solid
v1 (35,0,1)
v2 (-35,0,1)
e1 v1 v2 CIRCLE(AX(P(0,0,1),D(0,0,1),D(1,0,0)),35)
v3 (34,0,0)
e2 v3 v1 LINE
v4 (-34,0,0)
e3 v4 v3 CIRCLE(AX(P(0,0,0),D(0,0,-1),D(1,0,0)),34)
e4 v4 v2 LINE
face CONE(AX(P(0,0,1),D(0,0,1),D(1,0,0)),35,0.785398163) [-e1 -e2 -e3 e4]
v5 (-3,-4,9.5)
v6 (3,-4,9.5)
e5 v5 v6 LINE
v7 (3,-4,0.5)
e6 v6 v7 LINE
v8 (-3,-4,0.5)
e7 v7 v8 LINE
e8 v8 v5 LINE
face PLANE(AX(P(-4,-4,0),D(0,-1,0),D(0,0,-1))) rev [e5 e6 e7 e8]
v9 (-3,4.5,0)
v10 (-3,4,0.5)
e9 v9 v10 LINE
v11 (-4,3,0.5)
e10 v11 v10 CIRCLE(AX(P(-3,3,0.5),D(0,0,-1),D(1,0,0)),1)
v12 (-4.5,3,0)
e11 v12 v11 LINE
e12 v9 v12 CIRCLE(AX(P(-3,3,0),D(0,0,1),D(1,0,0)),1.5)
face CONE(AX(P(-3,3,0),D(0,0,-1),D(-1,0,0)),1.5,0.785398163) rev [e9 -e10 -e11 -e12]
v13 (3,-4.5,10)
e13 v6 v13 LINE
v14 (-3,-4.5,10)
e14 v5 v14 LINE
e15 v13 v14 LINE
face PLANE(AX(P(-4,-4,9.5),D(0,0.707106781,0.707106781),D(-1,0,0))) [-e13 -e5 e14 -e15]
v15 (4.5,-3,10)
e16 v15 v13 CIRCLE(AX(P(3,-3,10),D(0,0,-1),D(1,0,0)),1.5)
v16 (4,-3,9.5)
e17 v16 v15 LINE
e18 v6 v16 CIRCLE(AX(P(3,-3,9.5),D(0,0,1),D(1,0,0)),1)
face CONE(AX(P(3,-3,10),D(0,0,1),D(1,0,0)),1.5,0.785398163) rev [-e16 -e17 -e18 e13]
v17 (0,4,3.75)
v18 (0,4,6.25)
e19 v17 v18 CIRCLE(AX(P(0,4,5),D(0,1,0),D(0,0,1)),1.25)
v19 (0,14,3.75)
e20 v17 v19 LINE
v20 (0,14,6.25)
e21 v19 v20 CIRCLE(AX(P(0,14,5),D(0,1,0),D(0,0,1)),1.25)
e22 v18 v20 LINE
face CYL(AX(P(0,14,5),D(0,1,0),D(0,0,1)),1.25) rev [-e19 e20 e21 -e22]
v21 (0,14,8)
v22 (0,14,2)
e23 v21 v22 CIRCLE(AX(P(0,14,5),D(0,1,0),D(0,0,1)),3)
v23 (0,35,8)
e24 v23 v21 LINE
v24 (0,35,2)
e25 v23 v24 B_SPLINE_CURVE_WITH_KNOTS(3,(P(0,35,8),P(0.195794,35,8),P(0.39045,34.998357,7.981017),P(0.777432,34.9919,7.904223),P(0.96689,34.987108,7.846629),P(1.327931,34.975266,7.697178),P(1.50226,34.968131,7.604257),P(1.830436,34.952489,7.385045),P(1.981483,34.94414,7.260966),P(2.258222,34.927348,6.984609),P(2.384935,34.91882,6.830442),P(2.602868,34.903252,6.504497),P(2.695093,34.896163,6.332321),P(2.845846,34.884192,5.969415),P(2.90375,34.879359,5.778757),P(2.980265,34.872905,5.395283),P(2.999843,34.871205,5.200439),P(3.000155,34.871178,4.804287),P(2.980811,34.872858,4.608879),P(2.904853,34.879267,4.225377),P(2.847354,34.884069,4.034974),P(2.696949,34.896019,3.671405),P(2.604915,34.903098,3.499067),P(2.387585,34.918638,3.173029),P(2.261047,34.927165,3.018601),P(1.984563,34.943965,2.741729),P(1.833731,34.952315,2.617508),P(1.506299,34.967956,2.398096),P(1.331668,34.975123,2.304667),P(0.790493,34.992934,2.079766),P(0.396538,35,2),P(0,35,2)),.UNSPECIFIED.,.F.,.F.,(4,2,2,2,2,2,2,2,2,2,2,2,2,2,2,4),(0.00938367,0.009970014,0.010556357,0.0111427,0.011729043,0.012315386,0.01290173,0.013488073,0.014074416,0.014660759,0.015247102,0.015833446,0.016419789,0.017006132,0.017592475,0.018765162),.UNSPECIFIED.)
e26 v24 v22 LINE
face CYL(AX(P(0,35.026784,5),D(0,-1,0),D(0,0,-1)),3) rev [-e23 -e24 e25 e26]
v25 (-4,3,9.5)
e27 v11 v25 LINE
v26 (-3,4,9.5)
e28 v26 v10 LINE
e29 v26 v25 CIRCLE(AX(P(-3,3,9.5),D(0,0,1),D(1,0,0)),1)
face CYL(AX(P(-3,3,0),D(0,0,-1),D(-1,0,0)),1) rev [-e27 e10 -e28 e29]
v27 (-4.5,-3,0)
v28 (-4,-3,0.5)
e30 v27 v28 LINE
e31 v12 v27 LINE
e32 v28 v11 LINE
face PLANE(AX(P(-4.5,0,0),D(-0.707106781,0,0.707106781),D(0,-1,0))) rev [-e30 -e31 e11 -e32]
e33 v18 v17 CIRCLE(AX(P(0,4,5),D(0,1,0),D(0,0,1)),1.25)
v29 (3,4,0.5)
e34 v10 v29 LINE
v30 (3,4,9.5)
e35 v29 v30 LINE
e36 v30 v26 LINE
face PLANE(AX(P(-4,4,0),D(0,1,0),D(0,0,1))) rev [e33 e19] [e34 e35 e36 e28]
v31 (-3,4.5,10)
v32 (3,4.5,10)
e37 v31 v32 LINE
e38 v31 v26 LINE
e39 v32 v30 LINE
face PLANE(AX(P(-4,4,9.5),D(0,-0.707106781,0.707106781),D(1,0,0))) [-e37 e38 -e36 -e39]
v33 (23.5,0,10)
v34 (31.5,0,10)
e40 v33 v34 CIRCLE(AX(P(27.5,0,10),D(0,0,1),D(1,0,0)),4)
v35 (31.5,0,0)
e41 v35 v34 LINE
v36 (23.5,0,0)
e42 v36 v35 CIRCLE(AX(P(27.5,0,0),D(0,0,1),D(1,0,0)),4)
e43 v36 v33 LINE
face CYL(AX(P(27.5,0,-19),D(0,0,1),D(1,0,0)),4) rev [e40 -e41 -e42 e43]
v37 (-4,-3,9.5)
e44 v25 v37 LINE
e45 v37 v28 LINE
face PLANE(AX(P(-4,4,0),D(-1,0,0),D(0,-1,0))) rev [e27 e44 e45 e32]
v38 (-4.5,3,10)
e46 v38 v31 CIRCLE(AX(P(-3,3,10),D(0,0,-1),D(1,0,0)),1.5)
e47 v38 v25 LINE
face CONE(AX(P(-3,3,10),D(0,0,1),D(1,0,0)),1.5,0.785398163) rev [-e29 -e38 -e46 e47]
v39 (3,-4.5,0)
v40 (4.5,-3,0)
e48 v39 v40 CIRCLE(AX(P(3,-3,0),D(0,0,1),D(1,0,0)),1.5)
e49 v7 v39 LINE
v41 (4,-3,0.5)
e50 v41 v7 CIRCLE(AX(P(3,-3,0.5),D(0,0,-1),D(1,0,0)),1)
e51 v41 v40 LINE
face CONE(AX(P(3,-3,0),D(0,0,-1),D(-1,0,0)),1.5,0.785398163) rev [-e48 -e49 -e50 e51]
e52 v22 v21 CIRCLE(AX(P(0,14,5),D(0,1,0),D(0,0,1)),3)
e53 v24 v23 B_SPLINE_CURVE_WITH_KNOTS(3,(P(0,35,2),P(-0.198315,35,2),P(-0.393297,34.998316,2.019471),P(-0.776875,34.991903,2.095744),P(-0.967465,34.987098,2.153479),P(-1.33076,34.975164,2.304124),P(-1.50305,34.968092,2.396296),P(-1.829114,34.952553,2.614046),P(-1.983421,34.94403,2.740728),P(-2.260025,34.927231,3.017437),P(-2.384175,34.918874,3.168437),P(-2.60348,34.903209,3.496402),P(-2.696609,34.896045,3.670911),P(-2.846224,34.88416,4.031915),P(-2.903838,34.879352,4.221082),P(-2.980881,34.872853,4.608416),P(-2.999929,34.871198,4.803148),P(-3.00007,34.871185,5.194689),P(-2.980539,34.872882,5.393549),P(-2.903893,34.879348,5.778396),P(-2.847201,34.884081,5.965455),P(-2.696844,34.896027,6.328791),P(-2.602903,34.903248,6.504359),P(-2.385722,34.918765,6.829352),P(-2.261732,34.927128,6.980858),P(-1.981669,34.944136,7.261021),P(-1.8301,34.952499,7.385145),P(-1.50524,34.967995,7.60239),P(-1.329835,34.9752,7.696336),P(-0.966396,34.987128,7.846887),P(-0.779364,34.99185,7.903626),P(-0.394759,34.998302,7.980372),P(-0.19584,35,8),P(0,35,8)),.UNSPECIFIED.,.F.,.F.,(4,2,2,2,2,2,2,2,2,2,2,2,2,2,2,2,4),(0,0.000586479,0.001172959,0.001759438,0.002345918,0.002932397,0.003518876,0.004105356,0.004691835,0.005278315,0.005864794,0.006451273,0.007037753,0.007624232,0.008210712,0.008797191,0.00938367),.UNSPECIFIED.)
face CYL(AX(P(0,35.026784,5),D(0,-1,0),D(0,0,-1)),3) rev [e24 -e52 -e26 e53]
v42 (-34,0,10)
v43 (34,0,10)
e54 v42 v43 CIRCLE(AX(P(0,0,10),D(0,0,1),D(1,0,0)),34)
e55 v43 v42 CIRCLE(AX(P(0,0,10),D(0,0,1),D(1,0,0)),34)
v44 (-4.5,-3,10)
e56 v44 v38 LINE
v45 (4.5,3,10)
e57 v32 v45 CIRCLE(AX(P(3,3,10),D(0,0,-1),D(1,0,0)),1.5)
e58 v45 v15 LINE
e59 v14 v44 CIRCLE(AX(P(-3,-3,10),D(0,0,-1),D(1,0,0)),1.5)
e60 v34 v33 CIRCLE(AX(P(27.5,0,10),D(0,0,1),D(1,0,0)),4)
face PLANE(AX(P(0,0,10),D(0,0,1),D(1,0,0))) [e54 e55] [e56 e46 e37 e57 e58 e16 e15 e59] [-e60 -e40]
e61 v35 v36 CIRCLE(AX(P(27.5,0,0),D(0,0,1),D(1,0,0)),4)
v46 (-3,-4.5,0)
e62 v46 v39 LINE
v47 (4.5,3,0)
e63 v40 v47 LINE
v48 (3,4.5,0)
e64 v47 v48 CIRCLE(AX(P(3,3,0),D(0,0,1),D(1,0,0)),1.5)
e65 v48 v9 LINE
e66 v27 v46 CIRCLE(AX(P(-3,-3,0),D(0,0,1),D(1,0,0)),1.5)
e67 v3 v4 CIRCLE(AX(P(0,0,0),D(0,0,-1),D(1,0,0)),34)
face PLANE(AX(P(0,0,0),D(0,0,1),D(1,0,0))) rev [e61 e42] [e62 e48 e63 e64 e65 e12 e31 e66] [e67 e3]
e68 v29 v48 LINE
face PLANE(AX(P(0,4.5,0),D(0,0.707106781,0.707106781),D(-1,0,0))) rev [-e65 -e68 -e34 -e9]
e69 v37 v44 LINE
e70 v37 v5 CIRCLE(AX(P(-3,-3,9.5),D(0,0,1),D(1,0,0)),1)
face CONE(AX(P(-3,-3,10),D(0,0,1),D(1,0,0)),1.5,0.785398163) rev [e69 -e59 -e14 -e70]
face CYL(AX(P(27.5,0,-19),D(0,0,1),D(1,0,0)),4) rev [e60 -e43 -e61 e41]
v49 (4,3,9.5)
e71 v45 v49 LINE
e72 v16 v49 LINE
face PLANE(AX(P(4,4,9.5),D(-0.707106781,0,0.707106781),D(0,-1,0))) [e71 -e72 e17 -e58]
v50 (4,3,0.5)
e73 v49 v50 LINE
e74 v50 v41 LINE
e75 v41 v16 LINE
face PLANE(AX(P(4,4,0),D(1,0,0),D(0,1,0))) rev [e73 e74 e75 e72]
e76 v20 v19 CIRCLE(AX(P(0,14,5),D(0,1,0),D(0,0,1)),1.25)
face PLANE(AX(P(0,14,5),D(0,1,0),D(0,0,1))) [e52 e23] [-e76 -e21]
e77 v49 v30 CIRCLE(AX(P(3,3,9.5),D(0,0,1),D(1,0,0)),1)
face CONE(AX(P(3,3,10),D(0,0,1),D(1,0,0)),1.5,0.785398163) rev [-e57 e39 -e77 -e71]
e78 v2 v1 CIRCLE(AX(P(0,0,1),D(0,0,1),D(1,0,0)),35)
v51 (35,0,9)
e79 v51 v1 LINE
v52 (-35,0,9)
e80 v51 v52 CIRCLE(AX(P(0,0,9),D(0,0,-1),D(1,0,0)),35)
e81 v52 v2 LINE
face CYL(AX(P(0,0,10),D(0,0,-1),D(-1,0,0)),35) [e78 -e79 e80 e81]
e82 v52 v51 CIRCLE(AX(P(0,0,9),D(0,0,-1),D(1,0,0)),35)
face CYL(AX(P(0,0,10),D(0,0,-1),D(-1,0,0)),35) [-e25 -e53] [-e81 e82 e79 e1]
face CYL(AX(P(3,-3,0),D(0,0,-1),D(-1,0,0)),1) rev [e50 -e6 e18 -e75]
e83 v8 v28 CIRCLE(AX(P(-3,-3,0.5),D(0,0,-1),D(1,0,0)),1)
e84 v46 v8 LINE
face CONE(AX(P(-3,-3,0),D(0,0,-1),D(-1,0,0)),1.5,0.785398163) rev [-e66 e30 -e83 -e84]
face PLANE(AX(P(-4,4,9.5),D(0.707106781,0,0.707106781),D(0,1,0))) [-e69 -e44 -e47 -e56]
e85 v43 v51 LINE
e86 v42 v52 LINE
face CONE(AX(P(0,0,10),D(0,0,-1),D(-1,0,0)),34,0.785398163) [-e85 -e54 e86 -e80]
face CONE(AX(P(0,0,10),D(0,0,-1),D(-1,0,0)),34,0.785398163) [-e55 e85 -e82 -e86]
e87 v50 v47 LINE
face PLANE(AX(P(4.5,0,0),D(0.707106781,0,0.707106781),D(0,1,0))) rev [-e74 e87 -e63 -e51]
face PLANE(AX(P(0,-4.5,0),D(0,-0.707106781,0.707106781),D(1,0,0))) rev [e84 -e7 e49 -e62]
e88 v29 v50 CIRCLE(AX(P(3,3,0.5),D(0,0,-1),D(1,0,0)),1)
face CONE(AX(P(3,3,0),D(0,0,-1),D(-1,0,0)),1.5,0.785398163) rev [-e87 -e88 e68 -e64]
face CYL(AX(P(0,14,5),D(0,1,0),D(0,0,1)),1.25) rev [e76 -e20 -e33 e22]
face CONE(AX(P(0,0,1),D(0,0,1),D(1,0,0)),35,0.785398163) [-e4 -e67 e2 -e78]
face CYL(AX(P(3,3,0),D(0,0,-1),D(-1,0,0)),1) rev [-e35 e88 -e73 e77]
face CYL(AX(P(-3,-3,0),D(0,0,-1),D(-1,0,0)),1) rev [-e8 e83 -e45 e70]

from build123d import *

# Parameters (mm, degrees)
SKETCH1_R             = 35
BOSS_EXTRUDE1_DEPTH   = 10
CHAMFER1_SIZE         = 1
SKETCH2_R             = 1
CUT_EXTRUDE1_DEPTH    = 30
SKETCH3_R             = 4
CUT_EXTRUDE2_DEPTH    = 29
SKETCH4_W             = 8
SKETCH4_H             = 8
CUT_EXTRUDE3_DEPTH    = 51.497524692
FILLET1_R             = 1
SKETCH5_R             = 0.5
CUT_EXTRUDE4_DEPTH    = 54.347914673
SKETCH7_R             = 3
CUT_EXTRUDE5_DEPTH    = 62.040969986
M3_TAPPED_HOLE1_D     = 2.5
M3_TAPPED_HOLE1_DEPTH = 12
M3_TAPPED_HOLE1_TIP   = 0.751075774
CHAMFER2_SIZE         = 0.5


with BuildPart() as part:
    # Sketch1 → Boss-Extrude1 (new body)
    with BuildSketch(Plane.XY):
        Circle(SKETCH1_R)
    extrude(amount=BOSS_EXTRUDE1_DEPTH)

    # Chamfer1
    chamfer1_edges = [part.edges().sort_by_distance(p)[0] for p in [
        (-35, 0, 0),
        (-35, 0, 10),
    ]]
    chamfer(chamfer1_edges, length=CHAMFER1_SIZE)

    # Sketch2 → Cut-Extrude1 (cut)
    with BuildSketch(Plane.XY.offset(10)):
        Circle(SKETCH2_R)
    extrude(amount=-CUT_EXTRUDE1_DEPTH, mode=Mode.SUBTRACT)

    # Sketch3 → Cut-Extrude2 (cut)
    with BuildSketch(Plane.XY.offset(10)):
        with Locations((27.5, 0)):
            Circle(SKETCH3_R)
    extrude(amount=-CUT_EXTRUDE2_DEPTH, mode=Mode.SUBTRACT)

    # Sketch4 → Cut-Extrude3 (cut, through all)
    with BuildSketch(Plane.XY.offset(10)):
        Rectangle(SKETCH4_W, SKETCH4_H)
    extrude(amount=-CUT_EXTRUDE3_DEPTH, mode=Mode.SUBTRACT)

    # Fillet1
    fillet1_edges = [part.edges().sort_by_distance(p)[0] for p in [
        (4, 4, 5),
        (4, -4, 5),
        (-4, -4, 5),
        (-4, 4, 5),
    ]]
    fillet(fillet1_edges, radius=FILLET1_R)

    # Sketch5 → Cut-Extrude4 (cut, through all)
    with BuildSketch(Plane.XZ.offset(-4)):
        with Locations(Location((0, 5, 0), (0, 0, 270))):
            Circle(SKETCH5_R)
    extrude(amount=-CUT_EXTRUDE4_DEPTH, mode=Mode.SUBTRACT)

    # Sketch7 → Cut-Extrude5 (cut, through all)
    with BuildSketch(Plane(origin=(0, 14, 0), x_dir=(1, 0, 0), z_dir=(0, 1, 0))):
        with Locations(Location((0, -5, 0), (0, 0, 90))):
            Circle(SKETCH7_R)
    extrude(amount=CUT_EXTRUDE5_DEPTH, mode=Mode.SUBTRACT)

    # M3 Tapped Hole1
    with Locations(Plane(origin=(0, 14, 5), x_dir=(0, 0, 1), z_dir=(0, 1, 0))):
        with Locations((0, 0)):
            Hole(M3_TAPPED_HOLE1_D / 2, depth=M3_TAPPED_HOLE1_DEPTH)
            with Locations((0, 0, -(M3_TAPPED_HOLE1_DEPTH + M3_TAPPED_HOLE1_TIP / 2))):  # 118° drill point
                Cone(0, M3_TAPPED_HOLE1_D / 2, M3_TAPPED_HOLE1_TIP, mode=Mode.SUBTRACT)

    # Chamfer2
    chamfer2_edges = [part.edges().sort_by_distance(p)[0] for p in [
        (0, -4, 10),
        (0, -4, 0),
        (-4, 0, 10),
        (-4, 0, 0),
        (4, 0, 10),
        (4, 0, 0),
        (0, 4, 10),
        (0, 4, 0),
        (-3.707106781, -3.707106781, 10),
        (-3.707106781, -3.707106781, 0),
        (3.707106781, -3.707106781, 10),
        (3.707106781, -3.707106781, 0),
        (3.707106781, 3.707106781, 10),
        (3.707106781, 3.707106781, 0),
        (-3.707106781, 3.707106781, 10),
        (-3.707106781, 3.707106781, 0),
    ]]
    chamfer(chamfer2_edges, length=CHAMFER2_SIZE)


solid = part.part
